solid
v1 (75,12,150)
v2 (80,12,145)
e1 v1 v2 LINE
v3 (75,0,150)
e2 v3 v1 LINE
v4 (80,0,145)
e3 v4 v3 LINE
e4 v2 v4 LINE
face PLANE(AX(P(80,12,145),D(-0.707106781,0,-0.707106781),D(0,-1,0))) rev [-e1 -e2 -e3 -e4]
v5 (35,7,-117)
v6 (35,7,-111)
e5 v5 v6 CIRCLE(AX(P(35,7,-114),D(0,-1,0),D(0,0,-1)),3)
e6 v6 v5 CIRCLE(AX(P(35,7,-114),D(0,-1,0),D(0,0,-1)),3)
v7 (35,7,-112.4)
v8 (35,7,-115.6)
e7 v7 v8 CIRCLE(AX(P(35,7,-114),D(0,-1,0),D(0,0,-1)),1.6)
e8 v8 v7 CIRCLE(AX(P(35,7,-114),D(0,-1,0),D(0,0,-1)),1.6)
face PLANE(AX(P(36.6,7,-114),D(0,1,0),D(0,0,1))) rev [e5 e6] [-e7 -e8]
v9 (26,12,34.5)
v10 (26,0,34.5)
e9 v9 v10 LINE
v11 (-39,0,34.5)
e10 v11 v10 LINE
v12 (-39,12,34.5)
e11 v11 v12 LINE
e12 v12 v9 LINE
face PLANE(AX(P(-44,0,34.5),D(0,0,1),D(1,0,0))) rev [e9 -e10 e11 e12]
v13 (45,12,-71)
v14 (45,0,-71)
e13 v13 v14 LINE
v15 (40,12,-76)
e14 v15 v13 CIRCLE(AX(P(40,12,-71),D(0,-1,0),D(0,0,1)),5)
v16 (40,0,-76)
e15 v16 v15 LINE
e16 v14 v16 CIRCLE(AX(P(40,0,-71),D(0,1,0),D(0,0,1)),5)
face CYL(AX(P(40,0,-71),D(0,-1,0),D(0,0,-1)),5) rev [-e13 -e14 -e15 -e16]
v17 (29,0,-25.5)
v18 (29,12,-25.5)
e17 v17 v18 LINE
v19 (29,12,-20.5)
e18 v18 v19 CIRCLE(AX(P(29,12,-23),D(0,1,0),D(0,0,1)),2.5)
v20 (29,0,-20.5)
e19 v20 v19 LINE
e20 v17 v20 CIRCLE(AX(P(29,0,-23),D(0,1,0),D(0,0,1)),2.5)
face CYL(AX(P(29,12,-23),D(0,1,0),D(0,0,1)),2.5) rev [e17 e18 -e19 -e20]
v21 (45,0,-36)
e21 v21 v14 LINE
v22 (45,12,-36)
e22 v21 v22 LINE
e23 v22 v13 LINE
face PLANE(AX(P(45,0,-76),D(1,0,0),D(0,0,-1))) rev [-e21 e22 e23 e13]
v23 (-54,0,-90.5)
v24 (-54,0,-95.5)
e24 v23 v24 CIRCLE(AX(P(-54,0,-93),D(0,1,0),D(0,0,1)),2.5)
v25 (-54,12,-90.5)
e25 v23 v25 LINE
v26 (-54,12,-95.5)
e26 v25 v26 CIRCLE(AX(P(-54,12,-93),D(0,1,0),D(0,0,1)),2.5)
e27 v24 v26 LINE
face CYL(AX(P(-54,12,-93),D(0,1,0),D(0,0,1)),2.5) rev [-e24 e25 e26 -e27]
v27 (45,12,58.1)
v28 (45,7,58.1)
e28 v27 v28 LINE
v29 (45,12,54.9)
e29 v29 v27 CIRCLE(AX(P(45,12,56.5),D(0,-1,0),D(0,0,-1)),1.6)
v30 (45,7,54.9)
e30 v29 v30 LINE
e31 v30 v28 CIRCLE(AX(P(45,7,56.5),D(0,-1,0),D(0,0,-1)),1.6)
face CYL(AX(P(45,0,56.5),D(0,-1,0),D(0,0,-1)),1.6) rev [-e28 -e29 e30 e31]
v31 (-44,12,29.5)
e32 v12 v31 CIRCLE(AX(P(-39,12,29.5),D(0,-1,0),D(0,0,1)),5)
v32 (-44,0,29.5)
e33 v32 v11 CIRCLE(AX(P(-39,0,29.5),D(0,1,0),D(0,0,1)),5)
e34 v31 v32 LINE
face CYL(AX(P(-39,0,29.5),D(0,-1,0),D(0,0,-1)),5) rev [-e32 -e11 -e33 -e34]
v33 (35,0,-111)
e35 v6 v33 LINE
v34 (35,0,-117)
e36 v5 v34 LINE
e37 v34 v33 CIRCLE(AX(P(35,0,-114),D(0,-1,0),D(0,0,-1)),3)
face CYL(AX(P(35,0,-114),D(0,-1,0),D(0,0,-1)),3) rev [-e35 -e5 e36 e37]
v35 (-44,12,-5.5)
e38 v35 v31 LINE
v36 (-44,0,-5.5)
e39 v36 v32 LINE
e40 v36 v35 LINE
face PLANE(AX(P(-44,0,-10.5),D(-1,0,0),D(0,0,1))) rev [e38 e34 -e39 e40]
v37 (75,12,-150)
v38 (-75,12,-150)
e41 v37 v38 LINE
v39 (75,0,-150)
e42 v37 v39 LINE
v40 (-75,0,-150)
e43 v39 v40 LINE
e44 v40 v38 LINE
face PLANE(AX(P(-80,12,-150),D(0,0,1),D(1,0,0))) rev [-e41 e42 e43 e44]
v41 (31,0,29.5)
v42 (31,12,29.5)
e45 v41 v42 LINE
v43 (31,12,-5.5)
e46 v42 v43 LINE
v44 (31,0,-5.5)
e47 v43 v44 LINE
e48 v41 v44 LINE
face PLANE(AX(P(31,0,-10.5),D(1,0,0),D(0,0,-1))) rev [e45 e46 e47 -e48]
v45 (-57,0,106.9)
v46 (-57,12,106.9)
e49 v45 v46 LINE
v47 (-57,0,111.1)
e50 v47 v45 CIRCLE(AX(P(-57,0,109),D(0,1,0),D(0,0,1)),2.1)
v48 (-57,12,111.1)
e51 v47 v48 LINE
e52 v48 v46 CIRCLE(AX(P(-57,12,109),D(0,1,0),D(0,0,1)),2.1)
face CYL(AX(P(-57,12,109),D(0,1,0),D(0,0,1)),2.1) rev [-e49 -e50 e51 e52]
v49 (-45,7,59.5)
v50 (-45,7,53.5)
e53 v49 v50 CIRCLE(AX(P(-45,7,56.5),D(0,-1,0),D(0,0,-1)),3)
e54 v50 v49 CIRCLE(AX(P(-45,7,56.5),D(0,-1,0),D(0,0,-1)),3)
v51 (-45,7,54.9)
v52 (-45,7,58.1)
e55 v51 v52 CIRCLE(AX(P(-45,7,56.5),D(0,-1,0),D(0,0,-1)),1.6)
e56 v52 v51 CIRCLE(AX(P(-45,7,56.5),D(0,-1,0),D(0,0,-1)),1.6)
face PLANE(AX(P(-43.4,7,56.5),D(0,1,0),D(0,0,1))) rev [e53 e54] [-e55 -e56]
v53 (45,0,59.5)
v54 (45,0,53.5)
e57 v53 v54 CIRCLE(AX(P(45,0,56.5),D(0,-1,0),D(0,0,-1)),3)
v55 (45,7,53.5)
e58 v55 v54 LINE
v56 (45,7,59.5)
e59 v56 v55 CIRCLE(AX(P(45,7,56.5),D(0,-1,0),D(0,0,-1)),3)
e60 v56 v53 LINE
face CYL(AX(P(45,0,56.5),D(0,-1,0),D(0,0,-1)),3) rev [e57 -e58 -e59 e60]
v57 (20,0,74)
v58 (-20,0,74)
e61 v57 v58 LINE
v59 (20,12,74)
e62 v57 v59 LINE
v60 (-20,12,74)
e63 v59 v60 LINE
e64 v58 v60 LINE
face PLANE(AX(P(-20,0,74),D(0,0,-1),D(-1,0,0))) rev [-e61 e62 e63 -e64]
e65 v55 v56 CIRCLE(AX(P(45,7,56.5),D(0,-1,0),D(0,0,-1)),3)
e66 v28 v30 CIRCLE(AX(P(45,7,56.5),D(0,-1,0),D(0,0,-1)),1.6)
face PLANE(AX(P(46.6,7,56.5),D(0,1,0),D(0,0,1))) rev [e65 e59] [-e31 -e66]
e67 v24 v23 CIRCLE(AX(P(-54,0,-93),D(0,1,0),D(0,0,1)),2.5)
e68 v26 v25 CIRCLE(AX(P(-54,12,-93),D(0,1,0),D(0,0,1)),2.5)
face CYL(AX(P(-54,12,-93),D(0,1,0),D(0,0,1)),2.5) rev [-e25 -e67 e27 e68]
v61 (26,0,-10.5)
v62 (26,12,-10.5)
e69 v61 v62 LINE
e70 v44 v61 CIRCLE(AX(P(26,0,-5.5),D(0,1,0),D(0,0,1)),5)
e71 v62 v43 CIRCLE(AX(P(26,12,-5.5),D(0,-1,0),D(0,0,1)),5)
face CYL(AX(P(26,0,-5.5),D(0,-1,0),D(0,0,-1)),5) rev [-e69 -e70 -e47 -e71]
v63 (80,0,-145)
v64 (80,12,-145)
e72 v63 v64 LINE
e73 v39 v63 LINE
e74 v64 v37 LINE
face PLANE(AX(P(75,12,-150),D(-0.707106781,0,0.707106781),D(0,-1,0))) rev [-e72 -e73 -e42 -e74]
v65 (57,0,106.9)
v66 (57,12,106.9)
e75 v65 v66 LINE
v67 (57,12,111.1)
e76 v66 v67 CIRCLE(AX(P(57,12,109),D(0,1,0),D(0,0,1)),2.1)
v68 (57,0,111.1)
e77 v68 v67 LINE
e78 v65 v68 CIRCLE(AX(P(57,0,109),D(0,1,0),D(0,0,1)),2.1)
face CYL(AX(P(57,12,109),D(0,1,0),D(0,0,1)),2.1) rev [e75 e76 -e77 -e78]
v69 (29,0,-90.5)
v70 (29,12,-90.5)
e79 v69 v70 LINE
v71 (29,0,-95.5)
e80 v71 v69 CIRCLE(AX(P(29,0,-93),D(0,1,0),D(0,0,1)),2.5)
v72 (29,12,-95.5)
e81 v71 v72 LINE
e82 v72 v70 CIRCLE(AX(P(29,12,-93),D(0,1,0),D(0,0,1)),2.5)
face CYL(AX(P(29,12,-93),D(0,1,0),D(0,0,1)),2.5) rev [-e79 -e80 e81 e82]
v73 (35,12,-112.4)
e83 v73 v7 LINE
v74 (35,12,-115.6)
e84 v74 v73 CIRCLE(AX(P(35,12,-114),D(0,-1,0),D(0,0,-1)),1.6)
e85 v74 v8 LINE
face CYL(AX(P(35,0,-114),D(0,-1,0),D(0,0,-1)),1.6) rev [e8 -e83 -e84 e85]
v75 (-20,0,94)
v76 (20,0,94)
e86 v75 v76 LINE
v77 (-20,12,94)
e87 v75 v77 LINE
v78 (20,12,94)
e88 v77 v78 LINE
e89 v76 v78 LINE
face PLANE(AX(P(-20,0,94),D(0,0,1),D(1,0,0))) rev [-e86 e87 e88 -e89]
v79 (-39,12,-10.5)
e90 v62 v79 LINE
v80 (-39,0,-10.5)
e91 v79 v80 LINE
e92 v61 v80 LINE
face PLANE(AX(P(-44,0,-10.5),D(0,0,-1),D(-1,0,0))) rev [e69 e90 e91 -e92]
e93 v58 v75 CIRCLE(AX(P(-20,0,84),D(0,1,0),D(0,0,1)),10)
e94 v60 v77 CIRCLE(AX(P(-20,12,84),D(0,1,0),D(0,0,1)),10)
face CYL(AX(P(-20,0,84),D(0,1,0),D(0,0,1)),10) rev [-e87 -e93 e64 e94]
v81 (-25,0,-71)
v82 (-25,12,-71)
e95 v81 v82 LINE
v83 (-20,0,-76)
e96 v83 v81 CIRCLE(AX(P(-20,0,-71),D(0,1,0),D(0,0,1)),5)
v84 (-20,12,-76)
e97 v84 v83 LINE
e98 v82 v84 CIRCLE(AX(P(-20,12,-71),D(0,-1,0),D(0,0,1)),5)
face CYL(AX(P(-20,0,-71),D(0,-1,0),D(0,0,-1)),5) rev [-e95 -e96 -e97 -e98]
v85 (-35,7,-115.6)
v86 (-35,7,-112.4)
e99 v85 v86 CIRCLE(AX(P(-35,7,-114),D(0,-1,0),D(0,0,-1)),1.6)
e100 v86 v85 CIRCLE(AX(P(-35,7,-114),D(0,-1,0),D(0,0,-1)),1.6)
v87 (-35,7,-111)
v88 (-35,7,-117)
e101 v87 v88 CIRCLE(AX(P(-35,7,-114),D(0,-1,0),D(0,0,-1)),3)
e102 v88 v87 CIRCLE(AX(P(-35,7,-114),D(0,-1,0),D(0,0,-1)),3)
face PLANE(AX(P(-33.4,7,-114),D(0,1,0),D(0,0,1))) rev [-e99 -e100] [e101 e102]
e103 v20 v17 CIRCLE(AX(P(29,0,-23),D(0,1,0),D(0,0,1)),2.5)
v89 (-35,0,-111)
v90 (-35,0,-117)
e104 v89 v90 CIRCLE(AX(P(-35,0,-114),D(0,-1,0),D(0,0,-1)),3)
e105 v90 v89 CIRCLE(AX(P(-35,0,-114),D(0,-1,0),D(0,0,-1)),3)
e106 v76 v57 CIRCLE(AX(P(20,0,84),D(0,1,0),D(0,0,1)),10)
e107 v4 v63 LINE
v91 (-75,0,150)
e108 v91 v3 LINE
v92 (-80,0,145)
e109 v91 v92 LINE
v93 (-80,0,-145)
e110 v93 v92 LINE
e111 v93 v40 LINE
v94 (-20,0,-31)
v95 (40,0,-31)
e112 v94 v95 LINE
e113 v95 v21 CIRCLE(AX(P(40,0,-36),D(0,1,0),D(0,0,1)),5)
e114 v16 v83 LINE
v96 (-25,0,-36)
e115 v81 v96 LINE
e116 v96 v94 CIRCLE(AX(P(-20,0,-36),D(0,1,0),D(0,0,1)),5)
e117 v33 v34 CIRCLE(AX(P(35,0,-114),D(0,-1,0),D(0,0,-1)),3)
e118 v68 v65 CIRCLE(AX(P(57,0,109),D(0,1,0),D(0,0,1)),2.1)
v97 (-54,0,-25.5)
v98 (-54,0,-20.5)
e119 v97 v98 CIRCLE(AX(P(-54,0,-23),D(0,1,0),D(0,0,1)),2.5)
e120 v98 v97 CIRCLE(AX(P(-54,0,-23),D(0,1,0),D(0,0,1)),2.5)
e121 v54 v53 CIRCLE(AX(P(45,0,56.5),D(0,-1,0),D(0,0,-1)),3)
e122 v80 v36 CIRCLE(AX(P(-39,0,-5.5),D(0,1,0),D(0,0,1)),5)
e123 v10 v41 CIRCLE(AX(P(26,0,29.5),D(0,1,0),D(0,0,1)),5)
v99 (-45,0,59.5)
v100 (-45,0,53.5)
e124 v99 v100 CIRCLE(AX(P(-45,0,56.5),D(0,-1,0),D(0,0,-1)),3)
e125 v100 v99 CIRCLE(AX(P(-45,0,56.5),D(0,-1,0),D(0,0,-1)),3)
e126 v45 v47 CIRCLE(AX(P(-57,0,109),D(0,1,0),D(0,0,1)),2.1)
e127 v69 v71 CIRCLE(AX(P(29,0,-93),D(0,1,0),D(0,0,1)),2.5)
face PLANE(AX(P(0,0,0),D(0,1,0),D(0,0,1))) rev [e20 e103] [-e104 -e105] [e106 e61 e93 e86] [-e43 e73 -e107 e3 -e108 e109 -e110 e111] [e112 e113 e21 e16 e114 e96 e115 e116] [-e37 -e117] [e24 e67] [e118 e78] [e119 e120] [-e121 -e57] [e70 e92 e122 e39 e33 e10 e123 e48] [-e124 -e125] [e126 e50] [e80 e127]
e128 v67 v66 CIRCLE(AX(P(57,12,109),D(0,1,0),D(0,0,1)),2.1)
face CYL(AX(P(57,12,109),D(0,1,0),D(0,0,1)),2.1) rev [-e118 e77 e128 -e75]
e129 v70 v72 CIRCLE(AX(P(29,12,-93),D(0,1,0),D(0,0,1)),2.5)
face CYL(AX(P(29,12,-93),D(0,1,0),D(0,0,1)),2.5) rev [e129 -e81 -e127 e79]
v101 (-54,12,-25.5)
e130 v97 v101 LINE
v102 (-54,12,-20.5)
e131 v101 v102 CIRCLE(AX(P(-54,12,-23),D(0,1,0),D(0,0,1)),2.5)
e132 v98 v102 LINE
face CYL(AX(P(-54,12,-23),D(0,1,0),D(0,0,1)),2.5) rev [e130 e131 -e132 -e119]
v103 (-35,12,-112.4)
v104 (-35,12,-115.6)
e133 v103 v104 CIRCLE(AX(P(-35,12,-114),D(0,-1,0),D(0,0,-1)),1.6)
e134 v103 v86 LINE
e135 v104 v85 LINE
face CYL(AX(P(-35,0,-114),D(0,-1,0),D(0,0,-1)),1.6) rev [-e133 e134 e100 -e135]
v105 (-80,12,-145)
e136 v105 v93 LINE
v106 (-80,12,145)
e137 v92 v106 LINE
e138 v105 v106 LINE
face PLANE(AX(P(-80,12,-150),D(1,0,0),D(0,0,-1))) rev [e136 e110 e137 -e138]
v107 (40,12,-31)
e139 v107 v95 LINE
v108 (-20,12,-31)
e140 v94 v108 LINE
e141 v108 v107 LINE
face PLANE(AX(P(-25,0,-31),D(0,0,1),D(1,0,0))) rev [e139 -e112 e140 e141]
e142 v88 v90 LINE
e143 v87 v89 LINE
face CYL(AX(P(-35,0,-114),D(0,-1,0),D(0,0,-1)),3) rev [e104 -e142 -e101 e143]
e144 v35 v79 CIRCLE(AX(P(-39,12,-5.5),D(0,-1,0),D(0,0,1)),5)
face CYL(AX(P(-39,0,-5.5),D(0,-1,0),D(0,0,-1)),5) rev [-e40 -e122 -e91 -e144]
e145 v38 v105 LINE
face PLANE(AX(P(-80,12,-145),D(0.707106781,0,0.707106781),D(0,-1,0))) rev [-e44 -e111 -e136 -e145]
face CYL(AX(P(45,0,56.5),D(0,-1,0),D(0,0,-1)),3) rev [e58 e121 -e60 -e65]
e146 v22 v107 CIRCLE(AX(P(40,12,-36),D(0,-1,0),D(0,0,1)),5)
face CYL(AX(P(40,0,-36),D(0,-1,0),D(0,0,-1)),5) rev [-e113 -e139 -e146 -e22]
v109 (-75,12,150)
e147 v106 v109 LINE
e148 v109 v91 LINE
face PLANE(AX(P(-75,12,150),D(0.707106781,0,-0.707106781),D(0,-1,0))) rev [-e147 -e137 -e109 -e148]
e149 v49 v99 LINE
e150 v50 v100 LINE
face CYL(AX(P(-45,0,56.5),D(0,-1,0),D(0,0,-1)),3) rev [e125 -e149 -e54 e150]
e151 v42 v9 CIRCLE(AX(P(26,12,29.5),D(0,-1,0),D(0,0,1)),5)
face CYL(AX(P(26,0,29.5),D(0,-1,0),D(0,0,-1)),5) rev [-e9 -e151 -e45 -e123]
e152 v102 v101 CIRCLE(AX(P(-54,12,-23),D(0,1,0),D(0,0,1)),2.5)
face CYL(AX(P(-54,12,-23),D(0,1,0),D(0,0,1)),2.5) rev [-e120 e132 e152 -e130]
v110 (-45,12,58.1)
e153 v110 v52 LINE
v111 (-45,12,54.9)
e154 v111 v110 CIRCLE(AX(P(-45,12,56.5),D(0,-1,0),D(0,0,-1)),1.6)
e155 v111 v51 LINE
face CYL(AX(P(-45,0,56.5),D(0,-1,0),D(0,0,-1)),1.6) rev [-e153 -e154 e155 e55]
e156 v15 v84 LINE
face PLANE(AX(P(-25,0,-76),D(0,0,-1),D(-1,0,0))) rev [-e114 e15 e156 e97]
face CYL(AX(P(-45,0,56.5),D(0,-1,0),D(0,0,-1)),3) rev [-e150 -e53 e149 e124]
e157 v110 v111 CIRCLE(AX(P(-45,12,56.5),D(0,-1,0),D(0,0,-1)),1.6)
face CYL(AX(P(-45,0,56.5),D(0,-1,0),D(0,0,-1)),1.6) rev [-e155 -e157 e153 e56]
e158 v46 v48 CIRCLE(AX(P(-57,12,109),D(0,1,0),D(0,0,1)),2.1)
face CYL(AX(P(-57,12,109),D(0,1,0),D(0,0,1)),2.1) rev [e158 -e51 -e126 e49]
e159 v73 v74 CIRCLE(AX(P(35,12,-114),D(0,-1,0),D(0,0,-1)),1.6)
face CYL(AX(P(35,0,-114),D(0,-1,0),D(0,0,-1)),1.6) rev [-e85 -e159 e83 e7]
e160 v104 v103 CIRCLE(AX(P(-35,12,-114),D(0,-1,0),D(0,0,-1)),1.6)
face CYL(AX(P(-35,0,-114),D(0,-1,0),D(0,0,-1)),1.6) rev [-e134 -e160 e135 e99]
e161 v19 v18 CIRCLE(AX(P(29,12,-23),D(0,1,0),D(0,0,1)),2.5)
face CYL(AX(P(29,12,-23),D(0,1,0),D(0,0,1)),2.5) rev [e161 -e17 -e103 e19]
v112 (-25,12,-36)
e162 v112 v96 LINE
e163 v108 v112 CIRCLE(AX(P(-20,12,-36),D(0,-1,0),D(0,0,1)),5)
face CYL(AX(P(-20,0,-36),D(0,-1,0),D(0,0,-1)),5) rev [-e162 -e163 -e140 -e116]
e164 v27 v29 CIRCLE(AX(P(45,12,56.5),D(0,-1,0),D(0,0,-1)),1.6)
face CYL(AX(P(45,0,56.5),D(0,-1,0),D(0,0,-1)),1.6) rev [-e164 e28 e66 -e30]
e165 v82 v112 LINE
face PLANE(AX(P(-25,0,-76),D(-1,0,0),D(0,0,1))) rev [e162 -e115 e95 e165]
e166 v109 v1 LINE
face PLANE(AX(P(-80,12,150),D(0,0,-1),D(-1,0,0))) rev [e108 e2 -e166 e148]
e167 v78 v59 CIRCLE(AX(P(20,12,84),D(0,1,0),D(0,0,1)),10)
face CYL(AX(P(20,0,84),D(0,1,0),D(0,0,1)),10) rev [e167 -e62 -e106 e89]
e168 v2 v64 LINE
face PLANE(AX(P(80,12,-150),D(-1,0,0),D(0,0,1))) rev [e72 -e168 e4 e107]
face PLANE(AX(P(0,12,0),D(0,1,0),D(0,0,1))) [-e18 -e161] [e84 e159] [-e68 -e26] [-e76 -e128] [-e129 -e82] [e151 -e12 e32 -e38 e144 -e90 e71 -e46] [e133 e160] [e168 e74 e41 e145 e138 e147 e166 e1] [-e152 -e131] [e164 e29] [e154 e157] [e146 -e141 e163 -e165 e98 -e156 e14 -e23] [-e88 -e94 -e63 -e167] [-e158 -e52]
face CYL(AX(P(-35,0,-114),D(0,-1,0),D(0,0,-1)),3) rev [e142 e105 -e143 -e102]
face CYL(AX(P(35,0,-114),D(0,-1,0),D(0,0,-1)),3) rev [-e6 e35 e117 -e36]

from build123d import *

# Parameters (mm, degrees)
SKETCH_1_W                = 160
SKETCH_1_H                = 300
EXTRUDE_1_DEPTH           = 12
CUT_EXTRUDE_1_DEPTH       = 171.423003142
HOLE_WIZARD_3_D           = 3.2
HOLE_WIZARD_3_CBORE_D     = 6
HOLE_WIZARD_3_CBORE_DEPTH = 7
HOLE_WIZARD_M5_1_D        = 4.2
CHAMFER_1_SIZE            = 5
SKETCH_29_W               = 70
SKETCH_29_H               = 45
SKETCH_29_W_2             = 75
CUT_EXTRUDE_3_DEPTH       = 171.423003142
FILLET_1_R                = 5
HOLE_WIZARD_M6_1_D        = 5


with BuildPart() as part:
    # 草图1 → 凸台-拉伸1 (new body)
    with BuildSketch(Plane(origin=(0, 0, 0), x_dir=(1, 0, 0), z_dir=(0, 1, 0))):
        Rectangle(SKETCH_1_W, SKETCH_1_H)
    extrude(amount=EXTRUDE_1_DEPTH)

    # 草图6 → 切除-拉伸1 (cut, through all)
    with BuildSketch(Plane(origin=(0, 12, 0), x_dir=(1, 0, 0), z_dir=(0, 1, 0))):
        with BuildLine():
            Line((-20, -74), (20, -74))
            ThreePointArc((20, -74), (30, -84), (20, -94))
            Line((20, -94), (-20, -94))
            ThreePointArc((-20, -94), (-30, -84), (-20, -74))
        make_face()
    extrude(amount=-CUT_EXTRUDE_1_DEPTH, mode=Mode.SUBTRACT)

    # Hole Wizard 3 (through all)
    with Locations(Plane(origin=(0, 0, 0), x_dir=(-1, 0, 0), z_dir=(0, -1, 0))):
        with Locations((35, 114), (-35, 114), (45, -56.5), (-45, -56.5)):
            CounterBoreHole(HOLE_WIZARD_3_D / 2, HOLE_WIZARD_3_CBORE_D / 2, HOLE_WIZARD_3_CBORE_DEPTH)

    # M5 螺纹孔1 (through all)
    with Locations(Plane(origin=(0, 12, 0), x_dir=(1, 0, 0), z_dir=(0, 1, 0))):
        with Locations((-57, -109), (57, -109)):
            Hole(HOLE_WIZARD_M5_1_D / 2)

    # 倒角1
    chamfer_1_edges = [part.edges().sort_by_distance(p)[0] for p in [
        (80, 6, 150),
        (-80, 6, 150),
        (-80, 6, -150),
        (80, 6, -150),
    ]]
    chamfer(chamfer_1_edges, length=CHAMFER_1_SIZE)

    # 草图29 → 切除-拉伸3 (cut, through all)
    with BuildSketch(Plane(origin=(0, 12, 0), x_dir=(1, 0, 0), z_dir=(0, 1, 0))):
        with Locations((10, 53.5)):
            Rectangle(SKETCH_29_W, SKETCH_29_H)
        with Locations((-6.5, -12)):
            Rectangle(SKETCH_29_W_2, SKETCH_29_H)
    extrude(amount=-CUT_EXTRUDE_3_DEPTH, mode=Mode.SUBTRACT)

    # 圆角1
    fillet_1_edges = [part.edges().sort_by_distance(p)[0] for p in [
        (31, 6, -10.5),
        (31, 6, 34.5),
        (-44, 6, 34.5),
        (-44, 6, -10.5),
        (45, 6, -76),
        (45, 6, -31),
        (-25, 6, -31),
        (-25, 6, -76),
    ]]
    fillet(fillet_1_edges, radius=FILLET_1_R)

    # M6 螺纹孔1 (through all)
    with Locations(Plane(origin=(0, 12, 0), x_dir=(1, 0, 0), z_dir=(0, 1, 0))):
        with Locations((-54, 93), (29, 93), (-54, 23), (29, 23)):
            Hole(HOLE_WIZARD_M6_1_D / 2)


solid = part.part
